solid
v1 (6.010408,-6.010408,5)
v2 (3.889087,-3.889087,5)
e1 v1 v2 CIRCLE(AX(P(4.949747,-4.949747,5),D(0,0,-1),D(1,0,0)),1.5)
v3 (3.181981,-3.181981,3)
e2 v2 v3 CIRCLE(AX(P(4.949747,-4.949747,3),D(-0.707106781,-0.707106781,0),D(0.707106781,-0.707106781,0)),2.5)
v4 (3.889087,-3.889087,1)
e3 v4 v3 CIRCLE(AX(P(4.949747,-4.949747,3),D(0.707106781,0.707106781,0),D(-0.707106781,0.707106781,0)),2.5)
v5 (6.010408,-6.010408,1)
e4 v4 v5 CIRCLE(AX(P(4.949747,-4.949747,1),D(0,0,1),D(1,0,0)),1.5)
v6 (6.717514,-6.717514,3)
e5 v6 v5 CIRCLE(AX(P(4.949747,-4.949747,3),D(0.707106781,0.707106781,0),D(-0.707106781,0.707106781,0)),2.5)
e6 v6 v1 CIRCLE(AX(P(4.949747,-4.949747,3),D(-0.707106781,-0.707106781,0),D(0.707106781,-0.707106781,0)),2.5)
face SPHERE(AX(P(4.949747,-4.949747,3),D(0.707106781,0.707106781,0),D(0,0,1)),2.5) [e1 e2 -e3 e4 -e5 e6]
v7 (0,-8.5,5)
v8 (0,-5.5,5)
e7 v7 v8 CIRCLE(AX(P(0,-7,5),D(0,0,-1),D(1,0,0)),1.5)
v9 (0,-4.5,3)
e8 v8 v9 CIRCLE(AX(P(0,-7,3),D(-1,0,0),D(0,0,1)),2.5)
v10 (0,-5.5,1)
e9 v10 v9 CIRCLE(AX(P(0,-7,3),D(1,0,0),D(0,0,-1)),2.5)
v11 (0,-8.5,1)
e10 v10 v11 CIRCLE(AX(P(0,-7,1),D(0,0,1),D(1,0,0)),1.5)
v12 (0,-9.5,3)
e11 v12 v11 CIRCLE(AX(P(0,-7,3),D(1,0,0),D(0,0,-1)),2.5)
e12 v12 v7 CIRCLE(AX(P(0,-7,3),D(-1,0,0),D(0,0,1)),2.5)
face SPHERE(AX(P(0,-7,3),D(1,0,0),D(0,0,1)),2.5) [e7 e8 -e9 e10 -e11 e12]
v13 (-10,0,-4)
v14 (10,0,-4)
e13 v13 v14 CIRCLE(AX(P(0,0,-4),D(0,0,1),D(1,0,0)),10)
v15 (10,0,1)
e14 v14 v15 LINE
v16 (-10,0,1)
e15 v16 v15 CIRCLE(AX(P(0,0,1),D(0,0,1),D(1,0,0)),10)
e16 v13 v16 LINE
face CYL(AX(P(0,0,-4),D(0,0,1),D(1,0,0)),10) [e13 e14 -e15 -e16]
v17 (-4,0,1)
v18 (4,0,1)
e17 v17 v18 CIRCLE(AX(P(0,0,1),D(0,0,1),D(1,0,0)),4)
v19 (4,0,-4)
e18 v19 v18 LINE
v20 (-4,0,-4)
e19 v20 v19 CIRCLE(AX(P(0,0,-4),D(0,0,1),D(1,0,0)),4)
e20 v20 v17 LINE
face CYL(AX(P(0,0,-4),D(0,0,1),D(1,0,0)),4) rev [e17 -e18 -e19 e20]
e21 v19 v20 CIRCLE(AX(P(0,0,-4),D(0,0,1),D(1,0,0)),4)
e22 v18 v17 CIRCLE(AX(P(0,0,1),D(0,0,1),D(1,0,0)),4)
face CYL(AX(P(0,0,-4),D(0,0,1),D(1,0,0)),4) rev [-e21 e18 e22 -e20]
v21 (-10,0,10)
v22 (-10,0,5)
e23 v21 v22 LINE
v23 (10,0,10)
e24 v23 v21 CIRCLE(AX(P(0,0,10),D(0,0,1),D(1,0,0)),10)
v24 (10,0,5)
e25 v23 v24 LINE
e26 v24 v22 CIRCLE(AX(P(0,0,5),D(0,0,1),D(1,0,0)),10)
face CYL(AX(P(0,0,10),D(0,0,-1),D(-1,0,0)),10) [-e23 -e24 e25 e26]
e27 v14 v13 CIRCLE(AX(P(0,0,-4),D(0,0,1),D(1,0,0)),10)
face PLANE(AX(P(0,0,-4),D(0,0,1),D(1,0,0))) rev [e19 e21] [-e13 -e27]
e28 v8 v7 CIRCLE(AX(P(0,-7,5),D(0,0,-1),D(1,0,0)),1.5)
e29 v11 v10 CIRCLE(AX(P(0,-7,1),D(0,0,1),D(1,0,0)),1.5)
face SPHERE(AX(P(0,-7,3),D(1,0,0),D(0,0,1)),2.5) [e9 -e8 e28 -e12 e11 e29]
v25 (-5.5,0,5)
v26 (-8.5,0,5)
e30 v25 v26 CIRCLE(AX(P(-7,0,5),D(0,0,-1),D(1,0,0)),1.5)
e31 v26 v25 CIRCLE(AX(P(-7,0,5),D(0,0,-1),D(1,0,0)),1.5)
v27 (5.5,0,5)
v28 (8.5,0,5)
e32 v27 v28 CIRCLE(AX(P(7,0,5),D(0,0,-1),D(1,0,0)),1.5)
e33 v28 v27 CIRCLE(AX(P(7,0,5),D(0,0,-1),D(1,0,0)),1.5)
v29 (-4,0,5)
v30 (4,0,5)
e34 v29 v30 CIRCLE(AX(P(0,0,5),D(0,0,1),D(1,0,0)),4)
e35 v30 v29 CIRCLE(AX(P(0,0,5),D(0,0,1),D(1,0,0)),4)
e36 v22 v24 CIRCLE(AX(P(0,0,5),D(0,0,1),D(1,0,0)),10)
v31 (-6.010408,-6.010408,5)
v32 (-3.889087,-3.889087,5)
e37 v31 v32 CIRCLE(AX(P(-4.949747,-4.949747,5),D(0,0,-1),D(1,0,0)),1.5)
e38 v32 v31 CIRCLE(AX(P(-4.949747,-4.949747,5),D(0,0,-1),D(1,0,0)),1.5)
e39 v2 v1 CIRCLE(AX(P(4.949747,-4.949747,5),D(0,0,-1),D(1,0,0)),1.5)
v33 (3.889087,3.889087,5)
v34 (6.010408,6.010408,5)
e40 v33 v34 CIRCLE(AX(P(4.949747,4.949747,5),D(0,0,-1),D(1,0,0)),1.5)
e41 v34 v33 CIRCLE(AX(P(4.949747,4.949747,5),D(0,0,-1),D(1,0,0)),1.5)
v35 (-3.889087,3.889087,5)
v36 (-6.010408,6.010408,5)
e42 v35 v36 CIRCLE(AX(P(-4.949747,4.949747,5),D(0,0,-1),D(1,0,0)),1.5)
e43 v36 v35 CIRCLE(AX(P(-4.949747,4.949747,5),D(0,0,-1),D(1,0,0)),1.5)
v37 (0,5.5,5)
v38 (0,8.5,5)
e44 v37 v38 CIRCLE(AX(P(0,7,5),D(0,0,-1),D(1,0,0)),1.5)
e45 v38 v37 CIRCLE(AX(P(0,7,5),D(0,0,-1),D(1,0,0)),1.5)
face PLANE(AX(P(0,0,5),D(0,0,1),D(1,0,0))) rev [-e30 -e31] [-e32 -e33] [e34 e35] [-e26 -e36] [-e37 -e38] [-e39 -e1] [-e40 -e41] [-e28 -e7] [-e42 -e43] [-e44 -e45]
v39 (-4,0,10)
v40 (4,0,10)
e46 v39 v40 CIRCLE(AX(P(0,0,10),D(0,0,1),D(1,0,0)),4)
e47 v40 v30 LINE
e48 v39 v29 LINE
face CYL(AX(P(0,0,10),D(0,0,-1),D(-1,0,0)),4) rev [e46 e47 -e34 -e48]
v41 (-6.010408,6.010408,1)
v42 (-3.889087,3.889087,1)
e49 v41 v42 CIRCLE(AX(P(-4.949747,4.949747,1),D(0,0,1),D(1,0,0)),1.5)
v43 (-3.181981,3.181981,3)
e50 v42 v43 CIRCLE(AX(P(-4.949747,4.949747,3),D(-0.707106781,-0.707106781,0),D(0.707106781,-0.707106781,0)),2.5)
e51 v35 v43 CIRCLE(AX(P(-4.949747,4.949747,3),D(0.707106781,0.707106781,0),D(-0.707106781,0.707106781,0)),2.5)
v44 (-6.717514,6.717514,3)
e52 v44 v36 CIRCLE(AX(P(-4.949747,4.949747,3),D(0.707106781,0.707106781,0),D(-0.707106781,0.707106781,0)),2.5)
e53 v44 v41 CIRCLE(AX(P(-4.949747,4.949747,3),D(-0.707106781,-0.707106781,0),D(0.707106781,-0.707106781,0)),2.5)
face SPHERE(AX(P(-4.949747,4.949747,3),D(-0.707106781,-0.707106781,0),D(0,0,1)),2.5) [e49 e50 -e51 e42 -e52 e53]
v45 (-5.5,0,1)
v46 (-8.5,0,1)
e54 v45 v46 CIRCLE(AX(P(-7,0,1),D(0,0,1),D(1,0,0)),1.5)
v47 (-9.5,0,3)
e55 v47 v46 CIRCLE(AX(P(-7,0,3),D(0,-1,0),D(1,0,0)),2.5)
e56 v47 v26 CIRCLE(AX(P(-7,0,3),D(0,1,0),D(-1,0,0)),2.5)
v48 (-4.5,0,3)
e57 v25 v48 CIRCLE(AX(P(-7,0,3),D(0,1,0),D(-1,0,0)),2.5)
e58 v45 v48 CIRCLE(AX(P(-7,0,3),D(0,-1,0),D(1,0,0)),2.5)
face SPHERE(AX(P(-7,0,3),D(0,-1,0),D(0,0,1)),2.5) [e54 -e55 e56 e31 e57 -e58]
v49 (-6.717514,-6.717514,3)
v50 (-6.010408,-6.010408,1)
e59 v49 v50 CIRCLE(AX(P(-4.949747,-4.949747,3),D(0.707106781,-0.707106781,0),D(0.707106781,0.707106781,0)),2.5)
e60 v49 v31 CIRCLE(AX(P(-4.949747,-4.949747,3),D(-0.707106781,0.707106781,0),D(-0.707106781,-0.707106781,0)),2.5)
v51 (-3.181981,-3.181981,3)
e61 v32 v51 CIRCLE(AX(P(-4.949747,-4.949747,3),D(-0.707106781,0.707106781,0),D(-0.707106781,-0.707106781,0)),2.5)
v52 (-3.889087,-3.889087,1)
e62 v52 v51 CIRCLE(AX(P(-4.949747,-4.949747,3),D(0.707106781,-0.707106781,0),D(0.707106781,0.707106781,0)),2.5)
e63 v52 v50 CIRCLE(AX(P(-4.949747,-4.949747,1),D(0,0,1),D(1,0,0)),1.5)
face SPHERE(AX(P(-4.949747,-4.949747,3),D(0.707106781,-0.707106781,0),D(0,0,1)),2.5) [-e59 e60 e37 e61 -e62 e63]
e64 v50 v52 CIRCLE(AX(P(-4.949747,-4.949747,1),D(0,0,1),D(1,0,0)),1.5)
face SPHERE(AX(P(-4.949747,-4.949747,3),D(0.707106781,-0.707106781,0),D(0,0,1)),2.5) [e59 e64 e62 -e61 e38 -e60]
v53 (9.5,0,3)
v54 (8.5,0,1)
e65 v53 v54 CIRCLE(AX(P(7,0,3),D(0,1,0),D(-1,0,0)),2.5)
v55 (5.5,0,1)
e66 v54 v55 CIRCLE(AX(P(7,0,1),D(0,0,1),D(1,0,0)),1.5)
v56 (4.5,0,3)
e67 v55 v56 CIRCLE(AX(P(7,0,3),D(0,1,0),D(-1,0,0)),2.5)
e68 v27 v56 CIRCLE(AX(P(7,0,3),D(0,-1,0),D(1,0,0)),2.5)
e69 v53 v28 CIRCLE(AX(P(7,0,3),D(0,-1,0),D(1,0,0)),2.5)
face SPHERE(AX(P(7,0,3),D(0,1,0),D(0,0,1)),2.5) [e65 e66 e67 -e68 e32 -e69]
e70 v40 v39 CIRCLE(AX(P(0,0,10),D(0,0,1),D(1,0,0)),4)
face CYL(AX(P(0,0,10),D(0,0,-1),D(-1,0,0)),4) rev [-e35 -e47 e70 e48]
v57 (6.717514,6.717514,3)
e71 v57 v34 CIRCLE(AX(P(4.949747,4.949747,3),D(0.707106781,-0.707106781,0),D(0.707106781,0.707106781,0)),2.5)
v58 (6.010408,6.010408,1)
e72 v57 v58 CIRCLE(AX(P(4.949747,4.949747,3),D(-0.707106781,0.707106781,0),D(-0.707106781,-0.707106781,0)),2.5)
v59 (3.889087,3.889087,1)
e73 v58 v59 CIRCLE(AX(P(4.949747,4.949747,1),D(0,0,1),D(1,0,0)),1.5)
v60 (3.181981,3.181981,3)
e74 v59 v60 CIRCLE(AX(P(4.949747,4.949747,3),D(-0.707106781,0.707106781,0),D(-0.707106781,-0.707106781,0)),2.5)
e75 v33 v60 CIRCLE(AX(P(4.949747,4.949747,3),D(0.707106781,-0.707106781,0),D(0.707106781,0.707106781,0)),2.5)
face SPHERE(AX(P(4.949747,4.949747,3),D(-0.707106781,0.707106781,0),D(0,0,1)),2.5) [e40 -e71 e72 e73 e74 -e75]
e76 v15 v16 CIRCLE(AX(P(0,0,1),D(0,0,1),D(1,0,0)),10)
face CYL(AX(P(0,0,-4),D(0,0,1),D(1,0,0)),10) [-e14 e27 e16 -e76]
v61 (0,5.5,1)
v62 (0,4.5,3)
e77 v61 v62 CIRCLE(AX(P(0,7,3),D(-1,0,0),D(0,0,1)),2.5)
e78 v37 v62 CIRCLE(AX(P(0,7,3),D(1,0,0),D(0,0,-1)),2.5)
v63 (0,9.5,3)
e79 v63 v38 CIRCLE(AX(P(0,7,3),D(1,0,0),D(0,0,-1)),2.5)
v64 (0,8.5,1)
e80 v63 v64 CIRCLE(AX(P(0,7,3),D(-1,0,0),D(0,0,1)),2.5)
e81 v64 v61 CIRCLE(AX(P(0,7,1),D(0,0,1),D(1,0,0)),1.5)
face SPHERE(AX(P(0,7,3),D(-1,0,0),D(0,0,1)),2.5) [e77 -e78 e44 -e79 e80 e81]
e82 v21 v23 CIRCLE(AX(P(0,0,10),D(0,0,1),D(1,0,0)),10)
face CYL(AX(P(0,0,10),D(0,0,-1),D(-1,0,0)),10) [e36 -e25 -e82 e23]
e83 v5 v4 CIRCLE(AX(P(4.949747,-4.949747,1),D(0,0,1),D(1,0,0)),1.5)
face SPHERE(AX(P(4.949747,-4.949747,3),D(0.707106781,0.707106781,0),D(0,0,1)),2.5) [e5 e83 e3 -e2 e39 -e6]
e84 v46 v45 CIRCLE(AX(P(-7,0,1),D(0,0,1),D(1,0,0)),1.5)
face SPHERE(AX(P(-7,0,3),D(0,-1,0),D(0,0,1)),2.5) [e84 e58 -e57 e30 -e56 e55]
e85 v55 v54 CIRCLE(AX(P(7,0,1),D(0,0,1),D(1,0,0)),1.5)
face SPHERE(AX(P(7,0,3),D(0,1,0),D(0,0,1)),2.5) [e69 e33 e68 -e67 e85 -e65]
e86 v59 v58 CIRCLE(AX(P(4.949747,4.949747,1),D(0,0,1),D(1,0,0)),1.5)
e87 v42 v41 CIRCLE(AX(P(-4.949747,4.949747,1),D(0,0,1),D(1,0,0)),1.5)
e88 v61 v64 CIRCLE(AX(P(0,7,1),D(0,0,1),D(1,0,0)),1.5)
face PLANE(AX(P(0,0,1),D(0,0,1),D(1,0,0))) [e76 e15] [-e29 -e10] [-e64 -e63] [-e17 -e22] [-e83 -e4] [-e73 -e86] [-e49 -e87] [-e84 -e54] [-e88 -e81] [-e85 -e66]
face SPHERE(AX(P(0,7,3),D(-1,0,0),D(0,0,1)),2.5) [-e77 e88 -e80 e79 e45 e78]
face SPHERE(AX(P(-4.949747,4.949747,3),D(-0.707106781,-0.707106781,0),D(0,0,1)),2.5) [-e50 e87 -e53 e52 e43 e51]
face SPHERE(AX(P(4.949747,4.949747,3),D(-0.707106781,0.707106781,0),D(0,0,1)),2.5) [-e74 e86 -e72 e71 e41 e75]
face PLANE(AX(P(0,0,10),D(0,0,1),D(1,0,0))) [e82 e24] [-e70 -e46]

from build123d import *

# Parameters (mm, degrees)
BOSS_EXTRUDE1_START = 5
SKETCH1_R           = 10
SKETCH1_R_2         = 4
BOSS_EXTRUDE1_DEPTH = 5
CIRPATTERN2_COUNT   = 8
BOSS_EXTRUDE2_START = -4
SKETCH3_R           = 10
SKETCH3_R_2         = 4
BOSS_EXTRUDE2_DEPTH = 5


with BuildPart() as part:
    # Sketch1 → Boss-Extrude1 (new body)
    with BuildSketch(Plane.XY.offset(BOSS_EXTRUDE1_START)):
        Circle(SKETCH1_R)
        Circle(SKETCH1_R_2, mode=Mode.SUBTRACT)
    extrude(amount=BOSS_EXTRUDE1_DEPTH)

    # Sketch2 → Revolve1 (revolve)
    with BuildSketch(Plane(origin=(0, 0, 0), x_dir=(0, 0, -1), z_dir=(1, 0, 0))):
        with BuildLine():
            Line((-3, 4.5), (-3, 9.5))
            ThreePointArc((-3, 9.5), (-5.5, 7), (-3, 4.5))
        make_face()
    revolve1 = revolve(axis=Axis((0, 4.5, 3), (0, 1, 0)))

    # CirPattern2: Revolve1 ×8 about axis
    cirpattern2_axis = Axis((0, 0, 0), (0, 0, 1))
    for i in range(1, CIRPATTERN2_COUNT):
        add(revolve1.rotate(cirpattern2_axis, i * 360 / CIRPATTERN2_COUNT))

    # Sketch3 → Boss-Extrude2 (add)
    with BuildSketch(Plane.XY.offset(BOSS_EXTRUDE2_START)):
        Circle(SKETCH3_R)
        Circle(SKETCH3_R_2, mode=Mode.SUBTRACT)
    extrude(amount=BOSS_EXTRUDE2_DEPTH)


solid = part.part
